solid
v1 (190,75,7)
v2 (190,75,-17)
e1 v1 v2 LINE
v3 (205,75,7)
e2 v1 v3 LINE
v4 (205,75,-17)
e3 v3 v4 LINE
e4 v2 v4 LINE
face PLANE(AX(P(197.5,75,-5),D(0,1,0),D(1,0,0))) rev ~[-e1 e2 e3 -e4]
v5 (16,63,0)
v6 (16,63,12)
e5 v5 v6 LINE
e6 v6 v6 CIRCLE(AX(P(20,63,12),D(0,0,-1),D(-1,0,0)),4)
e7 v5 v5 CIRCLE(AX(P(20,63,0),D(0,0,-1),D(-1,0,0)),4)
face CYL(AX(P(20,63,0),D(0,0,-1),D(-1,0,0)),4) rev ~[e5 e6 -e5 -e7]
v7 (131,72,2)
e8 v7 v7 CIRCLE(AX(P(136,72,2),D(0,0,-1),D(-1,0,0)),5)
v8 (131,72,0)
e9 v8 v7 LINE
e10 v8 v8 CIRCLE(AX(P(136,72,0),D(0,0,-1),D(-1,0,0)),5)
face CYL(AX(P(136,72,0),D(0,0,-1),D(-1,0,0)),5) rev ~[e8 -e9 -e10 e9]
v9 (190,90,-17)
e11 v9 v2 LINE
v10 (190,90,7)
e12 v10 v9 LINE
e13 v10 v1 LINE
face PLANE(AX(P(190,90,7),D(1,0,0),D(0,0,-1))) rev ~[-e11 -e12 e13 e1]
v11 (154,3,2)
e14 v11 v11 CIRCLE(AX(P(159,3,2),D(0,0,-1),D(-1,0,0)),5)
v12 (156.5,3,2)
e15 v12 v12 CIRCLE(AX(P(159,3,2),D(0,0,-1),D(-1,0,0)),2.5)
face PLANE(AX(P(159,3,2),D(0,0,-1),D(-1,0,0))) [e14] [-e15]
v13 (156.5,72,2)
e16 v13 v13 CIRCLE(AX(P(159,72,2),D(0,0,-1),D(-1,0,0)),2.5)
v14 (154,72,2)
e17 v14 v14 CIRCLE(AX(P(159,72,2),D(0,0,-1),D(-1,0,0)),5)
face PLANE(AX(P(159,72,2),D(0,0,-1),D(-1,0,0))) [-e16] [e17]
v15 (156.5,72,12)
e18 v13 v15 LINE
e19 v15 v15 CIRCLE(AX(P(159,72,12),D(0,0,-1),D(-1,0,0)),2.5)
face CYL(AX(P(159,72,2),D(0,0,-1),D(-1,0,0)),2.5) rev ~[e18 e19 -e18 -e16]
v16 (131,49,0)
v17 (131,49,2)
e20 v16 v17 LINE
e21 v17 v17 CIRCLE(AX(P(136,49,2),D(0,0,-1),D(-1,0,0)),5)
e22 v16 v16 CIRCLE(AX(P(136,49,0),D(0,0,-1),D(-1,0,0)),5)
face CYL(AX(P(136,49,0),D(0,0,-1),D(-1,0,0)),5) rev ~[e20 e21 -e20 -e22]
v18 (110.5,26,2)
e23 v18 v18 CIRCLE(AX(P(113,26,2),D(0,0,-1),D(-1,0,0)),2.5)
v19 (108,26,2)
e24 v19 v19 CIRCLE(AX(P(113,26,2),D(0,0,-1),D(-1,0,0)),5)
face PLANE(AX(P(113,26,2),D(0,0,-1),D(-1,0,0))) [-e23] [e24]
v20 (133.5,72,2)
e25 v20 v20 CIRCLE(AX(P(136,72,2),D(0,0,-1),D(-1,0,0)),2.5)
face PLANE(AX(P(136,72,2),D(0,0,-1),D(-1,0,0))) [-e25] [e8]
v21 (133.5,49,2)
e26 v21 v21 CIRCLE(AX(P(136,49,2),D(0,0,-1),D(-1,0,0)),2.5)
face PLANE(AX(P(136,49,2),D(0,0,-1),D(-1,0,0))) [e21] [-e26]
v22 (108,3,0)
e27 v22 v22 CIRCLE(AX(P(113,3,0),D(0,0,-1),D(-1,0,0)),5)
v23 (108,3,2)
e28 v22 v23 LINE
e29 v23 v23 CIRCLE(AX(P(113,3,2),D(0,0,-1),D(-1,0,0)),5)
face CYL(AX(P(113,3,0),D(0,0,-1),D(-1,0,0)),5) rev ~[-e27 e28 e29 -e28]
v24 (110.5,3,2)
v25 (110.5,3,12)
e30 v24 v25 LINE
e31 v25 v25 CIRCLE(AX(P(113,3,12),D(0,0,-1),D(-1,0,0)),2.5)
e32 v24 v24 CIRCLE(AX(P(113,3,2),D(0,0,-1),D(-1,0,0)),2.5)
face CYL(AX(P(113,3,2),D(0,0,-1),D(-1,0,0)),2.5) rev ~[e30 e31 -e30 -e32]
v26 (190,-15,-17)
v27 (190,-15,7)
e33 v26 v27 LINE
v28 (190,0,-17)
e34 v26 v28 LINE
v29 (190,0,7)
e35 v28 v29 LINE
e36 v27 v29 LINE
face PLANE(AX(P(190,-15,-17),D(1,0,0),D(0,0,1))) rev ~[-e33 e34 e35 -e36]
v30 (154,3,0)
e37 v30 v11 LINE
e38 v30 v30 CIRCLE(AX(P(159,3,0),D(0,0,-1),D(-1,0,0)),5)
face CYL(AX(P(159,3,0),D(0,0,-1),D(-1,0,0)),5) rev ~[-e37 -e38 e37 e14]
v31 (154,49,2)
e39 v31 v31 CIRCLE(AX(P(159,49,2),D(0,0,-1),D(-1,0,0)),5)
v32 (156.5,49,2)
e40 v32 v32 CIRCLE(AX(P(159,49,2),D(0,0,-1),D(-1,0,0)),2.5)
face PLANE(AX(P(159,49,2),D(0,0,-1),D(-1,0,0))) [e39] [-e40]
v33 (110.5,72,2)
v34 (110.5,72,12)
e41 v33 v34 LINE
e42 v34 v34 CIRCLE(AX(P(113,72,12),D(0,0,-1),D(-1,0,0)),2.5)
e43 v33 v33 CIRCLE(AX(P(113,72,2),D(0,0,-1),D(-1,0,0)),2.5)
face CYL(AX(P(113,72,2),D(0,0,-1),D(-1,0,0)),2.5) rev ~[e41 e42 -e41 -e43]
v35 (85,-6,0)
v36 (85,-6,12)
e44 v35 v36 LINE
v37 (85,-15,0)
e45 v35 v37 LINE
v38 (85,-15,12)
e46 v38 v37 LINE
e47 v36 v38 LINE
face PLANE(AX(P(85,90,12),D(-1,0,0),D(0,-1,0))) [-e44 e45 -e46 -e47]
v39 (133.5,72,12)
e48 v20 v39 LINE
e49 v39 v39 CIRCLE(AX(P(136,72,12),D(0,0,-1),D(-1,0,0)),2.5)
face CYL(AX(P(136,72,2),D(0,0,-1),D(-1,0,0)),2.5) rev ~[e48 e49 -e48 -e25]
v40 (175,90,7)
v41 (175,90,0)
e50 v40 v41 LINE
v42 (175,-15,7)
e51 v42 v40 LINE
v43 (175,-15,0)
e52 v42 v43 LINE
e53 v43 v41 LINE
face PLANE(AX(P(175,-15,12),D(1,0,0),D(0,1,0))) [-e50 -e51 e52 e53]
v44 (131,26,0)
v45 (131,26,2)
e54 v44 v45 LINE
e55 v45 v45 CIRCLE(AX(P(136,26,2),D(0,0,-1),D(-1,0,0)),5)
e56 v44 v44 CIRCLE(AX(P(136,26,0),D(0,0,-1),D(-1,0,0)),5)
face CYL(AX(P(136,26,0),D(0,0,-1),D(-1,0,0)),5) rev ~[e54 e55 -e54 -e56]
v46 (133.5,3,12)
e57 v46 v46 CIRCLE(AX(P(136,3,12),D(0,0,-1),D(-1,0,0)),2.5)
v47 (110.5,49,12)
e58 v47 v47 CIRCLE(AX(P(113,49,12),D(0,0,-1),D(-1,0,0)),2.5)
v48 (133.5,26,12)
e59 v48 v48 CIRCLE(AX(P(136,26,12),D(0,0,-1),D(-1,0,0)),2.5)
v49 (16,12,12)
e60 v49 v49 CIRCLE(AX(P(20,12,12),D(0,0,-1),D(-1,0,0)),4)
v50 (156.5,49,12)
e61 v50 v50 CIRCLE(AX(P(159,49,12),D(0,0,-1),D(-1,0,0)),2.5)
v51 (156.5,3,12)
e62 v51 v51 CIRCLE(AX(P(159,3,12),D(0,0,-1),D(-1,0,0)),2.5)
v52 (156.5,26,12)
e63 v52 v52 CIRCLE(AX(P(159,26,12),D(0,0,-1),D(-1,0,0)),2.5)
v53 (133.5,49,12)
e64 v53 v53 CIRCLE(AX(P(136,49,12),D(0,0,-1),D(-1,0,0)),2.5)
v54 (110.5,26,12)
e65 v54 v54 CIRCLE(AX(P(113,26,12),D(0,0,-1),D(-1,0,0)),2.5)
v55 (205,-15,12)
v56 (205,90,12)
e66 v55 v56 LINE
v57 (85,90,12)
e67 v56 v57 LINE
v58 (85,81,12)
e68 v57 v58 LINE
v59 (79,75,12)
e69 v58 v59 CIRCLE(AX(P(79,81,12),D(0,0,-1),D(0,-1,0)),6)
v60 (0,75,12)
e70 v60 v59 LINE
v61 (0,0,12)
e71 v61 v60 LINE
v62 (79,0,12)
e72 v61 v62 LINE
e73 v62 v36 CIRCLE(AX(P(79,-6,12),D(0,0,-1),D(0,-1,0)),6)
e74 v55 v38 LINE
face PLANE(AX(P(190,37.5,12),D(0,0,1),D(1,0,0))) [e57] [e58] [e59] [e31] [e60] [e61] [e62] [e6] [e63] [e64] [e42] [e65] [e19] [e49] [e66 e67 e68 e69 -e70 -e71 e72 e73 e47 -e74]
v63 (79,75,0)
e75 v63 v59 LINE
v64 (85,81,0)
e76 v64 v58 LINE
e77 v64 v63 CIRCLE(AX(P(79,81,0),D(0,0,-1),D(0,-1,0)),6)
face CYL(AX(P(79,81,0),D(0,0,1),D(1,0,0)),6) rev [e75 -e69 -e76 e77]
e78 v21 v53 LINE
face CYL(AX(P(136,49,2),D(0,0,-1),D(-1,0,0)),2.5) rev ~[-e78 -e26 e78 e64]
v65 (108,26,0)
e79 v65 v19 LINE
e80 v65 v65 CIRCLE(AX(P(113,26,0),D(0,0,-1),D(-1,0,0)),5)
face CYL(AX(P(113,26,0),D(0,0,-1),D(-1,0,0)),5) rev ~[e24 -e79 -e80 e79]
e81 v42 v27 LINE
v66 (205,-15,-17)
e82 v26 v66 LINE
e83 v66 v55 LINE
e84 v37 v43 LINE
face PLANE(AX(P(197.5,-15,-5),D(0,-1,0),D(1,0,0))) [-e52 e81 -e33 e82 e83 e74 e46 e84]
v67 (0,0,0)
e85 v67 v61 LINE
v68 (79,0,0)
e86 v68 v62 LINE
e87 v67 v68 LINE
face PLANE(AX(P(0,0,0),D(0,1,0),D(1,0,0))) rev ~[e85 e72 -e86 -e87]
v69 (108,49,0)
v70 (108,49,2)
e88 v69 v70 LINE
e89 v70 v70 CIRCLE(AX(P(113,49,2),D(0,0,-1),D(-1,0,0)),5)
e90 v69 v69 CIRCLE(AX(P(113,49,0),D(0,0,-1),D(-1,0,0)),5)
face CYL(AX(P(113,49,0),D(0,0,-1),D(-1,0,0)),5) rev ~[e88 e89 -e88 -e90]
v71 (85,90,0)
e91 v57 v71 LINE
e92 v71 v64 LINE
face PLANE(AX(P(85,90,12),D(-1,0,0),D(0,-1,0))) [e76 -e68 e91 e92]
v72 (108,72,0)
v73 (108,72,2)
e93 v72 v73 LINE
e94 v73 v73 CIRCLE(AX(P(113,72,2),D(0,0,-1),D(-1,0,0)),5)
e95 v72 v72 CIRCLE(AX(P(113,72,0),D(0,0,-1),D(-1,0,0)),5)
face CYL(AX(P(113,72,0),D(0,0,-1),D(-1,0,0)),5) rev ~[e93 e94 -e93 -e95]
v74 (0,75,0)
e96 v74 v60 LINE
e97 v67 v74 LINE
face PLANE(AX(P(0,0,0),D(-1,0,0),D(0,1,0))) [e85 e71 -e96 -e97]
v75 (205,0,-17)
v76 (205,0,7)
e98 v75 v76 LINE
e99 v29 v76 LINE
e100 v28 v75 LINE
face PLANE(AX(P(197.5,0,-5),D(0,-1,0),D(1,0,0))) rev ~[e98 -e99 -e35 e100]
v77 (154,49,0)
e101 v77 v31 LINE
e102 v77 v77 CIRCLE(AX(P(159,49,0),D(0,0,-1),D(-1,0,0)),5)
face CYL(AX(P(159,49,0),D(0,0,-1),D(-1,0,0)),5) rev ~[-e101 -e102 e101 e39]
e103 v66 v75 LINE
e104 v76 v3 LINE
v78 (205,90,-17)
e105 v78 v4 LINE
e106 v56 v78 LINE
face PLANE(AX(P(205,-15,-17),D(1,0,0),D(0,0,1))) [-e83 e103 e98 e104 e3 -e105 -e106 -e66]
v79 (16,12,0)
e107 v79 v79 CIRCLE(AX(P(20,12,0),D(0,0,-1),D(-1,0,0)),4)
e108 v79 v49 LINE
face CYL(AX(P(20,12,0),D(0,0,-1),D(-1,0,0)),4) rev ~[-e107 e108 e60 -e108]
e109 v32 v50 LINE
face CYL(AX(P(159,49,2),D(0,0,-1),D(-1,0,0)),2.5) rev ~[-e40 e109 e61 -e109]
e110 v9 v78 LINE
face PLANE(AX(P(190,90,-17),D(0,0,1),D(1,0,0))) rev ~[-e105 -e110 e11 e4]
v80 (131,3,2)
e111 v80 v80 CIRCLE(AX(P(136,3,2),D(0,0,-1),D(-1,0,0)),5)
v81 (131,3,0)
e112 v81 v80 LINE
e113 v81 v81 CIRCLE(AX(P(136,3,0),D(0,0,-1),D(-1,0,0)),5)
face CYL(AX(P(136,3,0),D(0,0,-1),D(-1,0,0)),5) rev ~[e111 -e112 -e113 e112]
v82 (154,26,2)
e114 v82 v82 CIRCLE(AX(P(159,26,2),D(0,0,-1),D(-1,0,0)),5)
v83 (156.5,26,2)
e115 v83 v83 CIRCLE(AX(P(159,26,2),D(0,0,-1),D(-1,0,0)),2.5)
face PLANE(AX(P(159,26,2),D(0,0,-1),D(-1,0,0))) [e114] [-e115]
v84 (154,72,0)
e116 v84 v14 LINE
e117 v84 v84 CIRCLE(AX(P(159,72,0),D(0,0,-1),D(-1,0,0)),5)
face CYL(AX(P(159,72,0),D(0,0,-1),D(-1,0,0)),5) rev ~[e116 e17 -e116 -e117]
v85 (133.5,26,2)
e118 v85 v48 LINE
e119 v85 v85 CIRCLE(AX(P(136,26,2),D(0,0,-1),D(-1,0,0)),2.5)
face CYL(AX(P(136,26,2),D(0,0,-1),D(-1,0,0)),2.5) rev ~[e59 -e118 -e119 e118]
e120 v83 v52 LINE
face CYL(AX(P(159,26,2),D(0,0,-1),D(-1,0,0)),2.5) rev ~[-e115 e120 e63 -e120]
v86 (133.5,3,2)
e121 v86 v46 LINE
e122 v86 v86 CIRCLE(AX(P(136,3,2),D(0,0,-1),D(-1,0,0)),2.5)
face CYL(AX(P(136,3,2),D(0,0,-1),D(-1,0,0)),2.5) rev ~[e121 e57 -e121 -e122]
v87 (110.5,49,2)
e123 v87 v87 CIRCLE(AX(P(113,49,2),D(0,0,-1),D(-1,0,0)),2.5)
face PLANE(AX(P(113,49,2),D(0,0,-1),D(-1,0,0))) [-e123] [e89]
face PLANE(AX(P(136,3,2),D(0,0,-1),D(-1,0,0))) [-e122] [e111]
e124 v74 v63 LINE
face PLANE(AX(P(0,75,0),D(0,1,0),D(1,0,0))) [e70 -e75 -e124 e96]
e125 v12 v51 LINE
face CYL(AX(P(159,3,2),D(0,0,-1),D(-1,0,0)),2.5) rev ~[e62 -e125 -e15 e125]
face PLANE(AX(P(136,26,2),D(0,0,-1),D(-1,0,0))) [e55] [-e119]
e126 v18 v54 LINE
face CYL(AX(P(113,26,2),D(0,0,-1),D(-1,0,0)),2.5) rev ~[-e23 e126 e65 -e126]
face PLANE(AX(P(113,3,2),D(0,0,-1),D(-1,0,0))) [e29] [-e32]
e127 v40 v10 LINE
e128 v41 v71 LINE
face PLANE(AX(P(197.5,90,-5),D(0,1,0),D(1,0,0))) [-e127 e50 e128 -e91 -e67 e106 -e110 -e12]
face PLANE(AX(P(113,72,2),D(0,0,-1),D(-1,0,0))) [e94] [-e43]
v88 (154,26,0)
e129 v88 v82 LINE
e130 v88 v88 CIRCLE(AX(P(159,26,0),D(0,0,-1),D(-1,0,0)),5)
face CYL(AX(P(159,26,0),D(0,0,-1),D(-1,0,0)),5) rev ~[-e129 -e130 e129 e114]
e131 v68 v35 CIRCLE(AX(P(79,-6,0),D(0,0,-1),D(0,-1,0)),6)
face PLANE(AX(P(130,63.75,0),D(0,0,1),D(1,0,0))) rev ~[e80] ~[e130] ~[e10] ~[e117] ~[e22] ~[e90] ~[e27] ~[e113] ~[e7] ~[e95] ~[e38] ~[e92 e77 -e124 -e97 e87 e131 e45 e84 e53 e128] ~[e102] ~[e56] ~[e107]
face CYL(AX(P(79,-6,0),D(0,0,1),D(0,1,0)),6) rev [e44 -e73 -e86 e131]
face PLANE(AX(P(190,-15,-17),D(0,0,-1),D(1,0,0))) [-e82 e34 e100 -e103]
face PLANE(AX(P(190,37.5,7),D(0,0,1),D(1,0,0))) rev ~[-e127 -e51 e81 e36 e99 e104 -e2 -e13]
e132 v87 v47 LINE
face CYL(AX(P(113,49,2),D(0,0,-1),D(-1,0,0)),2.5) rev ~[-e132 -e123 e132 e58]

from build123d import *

# Parameters (mm, degrees)
BASE_PLATE_SKETCH_W       = 85
BASE_PLATE_SKETCH_H       = 75
BASE_PLATE_85X75_DEPTH    = 12
PLATE_EXTENSION_DEPTH     = 12
NOTCH_FILLET_R6_A_R       = 6
NOTCH_FILLET_R6_B_R       = 6
END_FLANGE_SKETCH_W       = 30
END_FLANGE_SKETCH_H       = 105
END_FLANGE_DEPTH          = 5
SIDE_TAB_1_SKETCH_W       = 15
SIDE_TAB_1_SKETCH_H       = 24
SIDE_TAB_1_DEPTH          = 15
SIDE_TAB_2_SKETCH_W       = 15
SIDE_TAB_2_SKETCH_H       = 24
SIDE_TAB_2_DEPTH          = 15
COUNTERBORE_GRID_SKETCH_R = 5
COUNTERBORES_12X_10_DEPTH = 2
HOLE_GRID_SKETCH_R        = 2.5
HOLE_GRID_12X_5_DEPTH     = 10
MOUNTING_HOLES_SKETCH_R   = 4
MOUNTING_HOLES_2X_8_DEPTH = 15


with BuildPart() as part:
    # Base Plate Sketch → Base Plate 85x75 (new body)
    with BuildSketch(Plane.XY):
        with Locations((42.5, 37.5)):
            Rectangle(BASE_PLATE_SKETCH_W, BASE_PLATE_SKETCH_H)
    extrude(amount=BASE_PLATE_85X75_DEPTH)

    # Plate Extension Sketch → Plate Extension (add)
    with BuildSketch(Plane.XY.offset(12)):
        Polygon((85, 75), (85, 37.5), (175, 37.5), (175, 90), (85, 90), align=None)
        Polygon((175, 37.5), (85, 37.5), (85, 0), (85, -15), (175, -15), align=None)
    extrude(amount=-PLATE_EXTENSION_DEPTH)

    # Notch Fillet R6 A
    notch_fillet_r6_a_edges = [part.edges().sort_by_distance(p)[0] for p in [
        (85, 75, 6),
    ]]
    fillet(notch_fillet_r6_a_edges, radius=NOTCH_FILLET_R6_A_R)

    # Notch Fillet R6 B
    notch_fillet_r6_b_edges = [part.edges().sort_by_distance(p)[0] for p in [
        (85, 0, 6),
    ]]
    fillet(notch_fillet_r6_b_edges, radius=NOTCH_FILLET_R6_B_R)

    # End Flange Sketch → End Flange (add)
    with BuildSketch(Plane.XY.offset(12)):
        with Locations((190, 37.5)):
            Rectangle(END_FLANGE_SKETCH_W, END_FLANGE_SKETCH_H)
    extrude(amount=-END_FLANGE_DEPTH)

    # Side Tab 1 Sketch → Side Tab 1 (add)
    with BuildSketch(Plane(origin=(0, 90, 0), x_dir=(1, 0, 0), z_dir=(0, 1, 0))):
        with Locations((197.5, 5)):
            Rectangle(SIDE_TAB_1_SKETCH_W, SIDE_TAB_1_SKETCH_H)
    extrude(amount=-SIDE_TAB_1_DEPTH)

    # Side Tab 2 Sketch → Side Tab 2 (add)
    with BuildSketch(Plane.XZ.offset(15)):
        with Locations((197.5, -5)):
            Rectangle(SIDE_TAB_2_SKETCH_W, SIDE_TAB_2_SKETCH_H)
    extrude(amount=-SIDE_TAB_2_DEPTH)

    # Counterbore Grid Sketch → Counterbores 12xØ10 (cut)
    with BuildSketch(Plane(origin=(0, 0, 0), x_dir=(-1, 0, 0), z_dir=(0, 0, -1))):
        with Locations((-159, 72)):
            Circle(COUNTERBORE_GRID_SKETCH_R)
        with Locations((-136, 72)):
            Circle(COUNTERBORE_GRID_SKETCH_R)
        with Locations((-113, 72)):
            Circle(COUNTERBORE_GRID_SKETCH_R)
        with Locations((-113, 49)):
            Circle(COUNTERBORE_GRID_SKETCH_R)
        with Locations((-136, 49)):
            Circle(COUNTERBORE_GRID_SKETCH_R)
        with Locations((-159, 49)):
            Circle(COUNTERBORE_GRID_SKETCH_R)
        with Locations((-159, 26)):
            Circle(COUNTERBORE_GRID_SKETCH_R)
        with Locations((-136, 26)):
            Circle(COUNTERBORE_GRID_SKETCH_R)
        with Locations((-113, 26)):
            Circle(COUNTERBORE_GRID_SKETCH_R)
        with Locations((-113, 3)):
            Circle(COUNTERBORE_GRID_SKETCH_R)
        with Locations((-136, 3)):
            Circle(COUNTERBORE_GRID_SKETCH_R)
        with Locations((-159, 3)):
            Circle(COUNTERBORE_GRID_SKETCH_R)
    extrude(amount=-COUNTERBORES_12X_10_DEPTH, mode=Mode.SUBTRACT)

    # Hole Grid Sketch → Hole Grid 12xØ5 (cut)
    with BuildSketch(Plane(origin=(0, 0, 2), x_dir=(-1, 0, 0), z_dir=(0, 0, -1))):
        with Locations((-159, 72)):
            Circle(HOLE_GRID_SKETCH_R)
        with Locations((-136, 72)):
            Circle(HOLE_GRID_SKETCH_R)
        with Locations((-113, 72)):
            Circle(HOLE_GRID_SKETCH_R)
        with Locations((-113, 49)):
            Circle(HOLE_GRID_SKETCH_R)
        with Locations((-136, 49)):
            Circle(HOLE_GRID_SKETCH_R)
        with Locations((-159, 49)):
            Circle(HOLE_GRID_SKETCH_R)
        with Locations((-159, 26)):
            Circle(HOLE_GRID_SKETCH_R)
        with Locations((-136, 26)):
            Circle(HOLE_GRID_SKETCH_R)
        with Locations((-113, 26)):
            Circle(HOLE_GRID_SKETCH_R)
        with Locations((-159, 3)):
            Circle(HOLE_GRID_SKETCH_R)
        with Locations((-136, 3)):
            Circle(HOLE_GRID_SKETCH_R)
        with Locations((-113, 3)):
            Circle(HOLE_GRID_SKETCH_R)
    extrude(amount=-HOLE_GRID_12X_5_DEPTH, mode=Mode.SUBTRACT)

    # Mounting Holes Sketch → Mounting Holes 2xØ8 (cut)
    with BuildSketch(Plane(origin=(0, 0, 0), x_dir=(-1, 0, 0), z_dir=(0, 0, -1))):
        with Locations((-20, 63)):
            Circle(MOUNTING_HOLES_SKETCH_R)
        with Locations((-20, 12)):
            Circle(MOUNTING_HOLES_SKETCH_R)
    extrude(amount=-MOUNTING_HOLES_2X_8_DEPTH, mode=Mode.SUBTRACT)


solid = part.part
